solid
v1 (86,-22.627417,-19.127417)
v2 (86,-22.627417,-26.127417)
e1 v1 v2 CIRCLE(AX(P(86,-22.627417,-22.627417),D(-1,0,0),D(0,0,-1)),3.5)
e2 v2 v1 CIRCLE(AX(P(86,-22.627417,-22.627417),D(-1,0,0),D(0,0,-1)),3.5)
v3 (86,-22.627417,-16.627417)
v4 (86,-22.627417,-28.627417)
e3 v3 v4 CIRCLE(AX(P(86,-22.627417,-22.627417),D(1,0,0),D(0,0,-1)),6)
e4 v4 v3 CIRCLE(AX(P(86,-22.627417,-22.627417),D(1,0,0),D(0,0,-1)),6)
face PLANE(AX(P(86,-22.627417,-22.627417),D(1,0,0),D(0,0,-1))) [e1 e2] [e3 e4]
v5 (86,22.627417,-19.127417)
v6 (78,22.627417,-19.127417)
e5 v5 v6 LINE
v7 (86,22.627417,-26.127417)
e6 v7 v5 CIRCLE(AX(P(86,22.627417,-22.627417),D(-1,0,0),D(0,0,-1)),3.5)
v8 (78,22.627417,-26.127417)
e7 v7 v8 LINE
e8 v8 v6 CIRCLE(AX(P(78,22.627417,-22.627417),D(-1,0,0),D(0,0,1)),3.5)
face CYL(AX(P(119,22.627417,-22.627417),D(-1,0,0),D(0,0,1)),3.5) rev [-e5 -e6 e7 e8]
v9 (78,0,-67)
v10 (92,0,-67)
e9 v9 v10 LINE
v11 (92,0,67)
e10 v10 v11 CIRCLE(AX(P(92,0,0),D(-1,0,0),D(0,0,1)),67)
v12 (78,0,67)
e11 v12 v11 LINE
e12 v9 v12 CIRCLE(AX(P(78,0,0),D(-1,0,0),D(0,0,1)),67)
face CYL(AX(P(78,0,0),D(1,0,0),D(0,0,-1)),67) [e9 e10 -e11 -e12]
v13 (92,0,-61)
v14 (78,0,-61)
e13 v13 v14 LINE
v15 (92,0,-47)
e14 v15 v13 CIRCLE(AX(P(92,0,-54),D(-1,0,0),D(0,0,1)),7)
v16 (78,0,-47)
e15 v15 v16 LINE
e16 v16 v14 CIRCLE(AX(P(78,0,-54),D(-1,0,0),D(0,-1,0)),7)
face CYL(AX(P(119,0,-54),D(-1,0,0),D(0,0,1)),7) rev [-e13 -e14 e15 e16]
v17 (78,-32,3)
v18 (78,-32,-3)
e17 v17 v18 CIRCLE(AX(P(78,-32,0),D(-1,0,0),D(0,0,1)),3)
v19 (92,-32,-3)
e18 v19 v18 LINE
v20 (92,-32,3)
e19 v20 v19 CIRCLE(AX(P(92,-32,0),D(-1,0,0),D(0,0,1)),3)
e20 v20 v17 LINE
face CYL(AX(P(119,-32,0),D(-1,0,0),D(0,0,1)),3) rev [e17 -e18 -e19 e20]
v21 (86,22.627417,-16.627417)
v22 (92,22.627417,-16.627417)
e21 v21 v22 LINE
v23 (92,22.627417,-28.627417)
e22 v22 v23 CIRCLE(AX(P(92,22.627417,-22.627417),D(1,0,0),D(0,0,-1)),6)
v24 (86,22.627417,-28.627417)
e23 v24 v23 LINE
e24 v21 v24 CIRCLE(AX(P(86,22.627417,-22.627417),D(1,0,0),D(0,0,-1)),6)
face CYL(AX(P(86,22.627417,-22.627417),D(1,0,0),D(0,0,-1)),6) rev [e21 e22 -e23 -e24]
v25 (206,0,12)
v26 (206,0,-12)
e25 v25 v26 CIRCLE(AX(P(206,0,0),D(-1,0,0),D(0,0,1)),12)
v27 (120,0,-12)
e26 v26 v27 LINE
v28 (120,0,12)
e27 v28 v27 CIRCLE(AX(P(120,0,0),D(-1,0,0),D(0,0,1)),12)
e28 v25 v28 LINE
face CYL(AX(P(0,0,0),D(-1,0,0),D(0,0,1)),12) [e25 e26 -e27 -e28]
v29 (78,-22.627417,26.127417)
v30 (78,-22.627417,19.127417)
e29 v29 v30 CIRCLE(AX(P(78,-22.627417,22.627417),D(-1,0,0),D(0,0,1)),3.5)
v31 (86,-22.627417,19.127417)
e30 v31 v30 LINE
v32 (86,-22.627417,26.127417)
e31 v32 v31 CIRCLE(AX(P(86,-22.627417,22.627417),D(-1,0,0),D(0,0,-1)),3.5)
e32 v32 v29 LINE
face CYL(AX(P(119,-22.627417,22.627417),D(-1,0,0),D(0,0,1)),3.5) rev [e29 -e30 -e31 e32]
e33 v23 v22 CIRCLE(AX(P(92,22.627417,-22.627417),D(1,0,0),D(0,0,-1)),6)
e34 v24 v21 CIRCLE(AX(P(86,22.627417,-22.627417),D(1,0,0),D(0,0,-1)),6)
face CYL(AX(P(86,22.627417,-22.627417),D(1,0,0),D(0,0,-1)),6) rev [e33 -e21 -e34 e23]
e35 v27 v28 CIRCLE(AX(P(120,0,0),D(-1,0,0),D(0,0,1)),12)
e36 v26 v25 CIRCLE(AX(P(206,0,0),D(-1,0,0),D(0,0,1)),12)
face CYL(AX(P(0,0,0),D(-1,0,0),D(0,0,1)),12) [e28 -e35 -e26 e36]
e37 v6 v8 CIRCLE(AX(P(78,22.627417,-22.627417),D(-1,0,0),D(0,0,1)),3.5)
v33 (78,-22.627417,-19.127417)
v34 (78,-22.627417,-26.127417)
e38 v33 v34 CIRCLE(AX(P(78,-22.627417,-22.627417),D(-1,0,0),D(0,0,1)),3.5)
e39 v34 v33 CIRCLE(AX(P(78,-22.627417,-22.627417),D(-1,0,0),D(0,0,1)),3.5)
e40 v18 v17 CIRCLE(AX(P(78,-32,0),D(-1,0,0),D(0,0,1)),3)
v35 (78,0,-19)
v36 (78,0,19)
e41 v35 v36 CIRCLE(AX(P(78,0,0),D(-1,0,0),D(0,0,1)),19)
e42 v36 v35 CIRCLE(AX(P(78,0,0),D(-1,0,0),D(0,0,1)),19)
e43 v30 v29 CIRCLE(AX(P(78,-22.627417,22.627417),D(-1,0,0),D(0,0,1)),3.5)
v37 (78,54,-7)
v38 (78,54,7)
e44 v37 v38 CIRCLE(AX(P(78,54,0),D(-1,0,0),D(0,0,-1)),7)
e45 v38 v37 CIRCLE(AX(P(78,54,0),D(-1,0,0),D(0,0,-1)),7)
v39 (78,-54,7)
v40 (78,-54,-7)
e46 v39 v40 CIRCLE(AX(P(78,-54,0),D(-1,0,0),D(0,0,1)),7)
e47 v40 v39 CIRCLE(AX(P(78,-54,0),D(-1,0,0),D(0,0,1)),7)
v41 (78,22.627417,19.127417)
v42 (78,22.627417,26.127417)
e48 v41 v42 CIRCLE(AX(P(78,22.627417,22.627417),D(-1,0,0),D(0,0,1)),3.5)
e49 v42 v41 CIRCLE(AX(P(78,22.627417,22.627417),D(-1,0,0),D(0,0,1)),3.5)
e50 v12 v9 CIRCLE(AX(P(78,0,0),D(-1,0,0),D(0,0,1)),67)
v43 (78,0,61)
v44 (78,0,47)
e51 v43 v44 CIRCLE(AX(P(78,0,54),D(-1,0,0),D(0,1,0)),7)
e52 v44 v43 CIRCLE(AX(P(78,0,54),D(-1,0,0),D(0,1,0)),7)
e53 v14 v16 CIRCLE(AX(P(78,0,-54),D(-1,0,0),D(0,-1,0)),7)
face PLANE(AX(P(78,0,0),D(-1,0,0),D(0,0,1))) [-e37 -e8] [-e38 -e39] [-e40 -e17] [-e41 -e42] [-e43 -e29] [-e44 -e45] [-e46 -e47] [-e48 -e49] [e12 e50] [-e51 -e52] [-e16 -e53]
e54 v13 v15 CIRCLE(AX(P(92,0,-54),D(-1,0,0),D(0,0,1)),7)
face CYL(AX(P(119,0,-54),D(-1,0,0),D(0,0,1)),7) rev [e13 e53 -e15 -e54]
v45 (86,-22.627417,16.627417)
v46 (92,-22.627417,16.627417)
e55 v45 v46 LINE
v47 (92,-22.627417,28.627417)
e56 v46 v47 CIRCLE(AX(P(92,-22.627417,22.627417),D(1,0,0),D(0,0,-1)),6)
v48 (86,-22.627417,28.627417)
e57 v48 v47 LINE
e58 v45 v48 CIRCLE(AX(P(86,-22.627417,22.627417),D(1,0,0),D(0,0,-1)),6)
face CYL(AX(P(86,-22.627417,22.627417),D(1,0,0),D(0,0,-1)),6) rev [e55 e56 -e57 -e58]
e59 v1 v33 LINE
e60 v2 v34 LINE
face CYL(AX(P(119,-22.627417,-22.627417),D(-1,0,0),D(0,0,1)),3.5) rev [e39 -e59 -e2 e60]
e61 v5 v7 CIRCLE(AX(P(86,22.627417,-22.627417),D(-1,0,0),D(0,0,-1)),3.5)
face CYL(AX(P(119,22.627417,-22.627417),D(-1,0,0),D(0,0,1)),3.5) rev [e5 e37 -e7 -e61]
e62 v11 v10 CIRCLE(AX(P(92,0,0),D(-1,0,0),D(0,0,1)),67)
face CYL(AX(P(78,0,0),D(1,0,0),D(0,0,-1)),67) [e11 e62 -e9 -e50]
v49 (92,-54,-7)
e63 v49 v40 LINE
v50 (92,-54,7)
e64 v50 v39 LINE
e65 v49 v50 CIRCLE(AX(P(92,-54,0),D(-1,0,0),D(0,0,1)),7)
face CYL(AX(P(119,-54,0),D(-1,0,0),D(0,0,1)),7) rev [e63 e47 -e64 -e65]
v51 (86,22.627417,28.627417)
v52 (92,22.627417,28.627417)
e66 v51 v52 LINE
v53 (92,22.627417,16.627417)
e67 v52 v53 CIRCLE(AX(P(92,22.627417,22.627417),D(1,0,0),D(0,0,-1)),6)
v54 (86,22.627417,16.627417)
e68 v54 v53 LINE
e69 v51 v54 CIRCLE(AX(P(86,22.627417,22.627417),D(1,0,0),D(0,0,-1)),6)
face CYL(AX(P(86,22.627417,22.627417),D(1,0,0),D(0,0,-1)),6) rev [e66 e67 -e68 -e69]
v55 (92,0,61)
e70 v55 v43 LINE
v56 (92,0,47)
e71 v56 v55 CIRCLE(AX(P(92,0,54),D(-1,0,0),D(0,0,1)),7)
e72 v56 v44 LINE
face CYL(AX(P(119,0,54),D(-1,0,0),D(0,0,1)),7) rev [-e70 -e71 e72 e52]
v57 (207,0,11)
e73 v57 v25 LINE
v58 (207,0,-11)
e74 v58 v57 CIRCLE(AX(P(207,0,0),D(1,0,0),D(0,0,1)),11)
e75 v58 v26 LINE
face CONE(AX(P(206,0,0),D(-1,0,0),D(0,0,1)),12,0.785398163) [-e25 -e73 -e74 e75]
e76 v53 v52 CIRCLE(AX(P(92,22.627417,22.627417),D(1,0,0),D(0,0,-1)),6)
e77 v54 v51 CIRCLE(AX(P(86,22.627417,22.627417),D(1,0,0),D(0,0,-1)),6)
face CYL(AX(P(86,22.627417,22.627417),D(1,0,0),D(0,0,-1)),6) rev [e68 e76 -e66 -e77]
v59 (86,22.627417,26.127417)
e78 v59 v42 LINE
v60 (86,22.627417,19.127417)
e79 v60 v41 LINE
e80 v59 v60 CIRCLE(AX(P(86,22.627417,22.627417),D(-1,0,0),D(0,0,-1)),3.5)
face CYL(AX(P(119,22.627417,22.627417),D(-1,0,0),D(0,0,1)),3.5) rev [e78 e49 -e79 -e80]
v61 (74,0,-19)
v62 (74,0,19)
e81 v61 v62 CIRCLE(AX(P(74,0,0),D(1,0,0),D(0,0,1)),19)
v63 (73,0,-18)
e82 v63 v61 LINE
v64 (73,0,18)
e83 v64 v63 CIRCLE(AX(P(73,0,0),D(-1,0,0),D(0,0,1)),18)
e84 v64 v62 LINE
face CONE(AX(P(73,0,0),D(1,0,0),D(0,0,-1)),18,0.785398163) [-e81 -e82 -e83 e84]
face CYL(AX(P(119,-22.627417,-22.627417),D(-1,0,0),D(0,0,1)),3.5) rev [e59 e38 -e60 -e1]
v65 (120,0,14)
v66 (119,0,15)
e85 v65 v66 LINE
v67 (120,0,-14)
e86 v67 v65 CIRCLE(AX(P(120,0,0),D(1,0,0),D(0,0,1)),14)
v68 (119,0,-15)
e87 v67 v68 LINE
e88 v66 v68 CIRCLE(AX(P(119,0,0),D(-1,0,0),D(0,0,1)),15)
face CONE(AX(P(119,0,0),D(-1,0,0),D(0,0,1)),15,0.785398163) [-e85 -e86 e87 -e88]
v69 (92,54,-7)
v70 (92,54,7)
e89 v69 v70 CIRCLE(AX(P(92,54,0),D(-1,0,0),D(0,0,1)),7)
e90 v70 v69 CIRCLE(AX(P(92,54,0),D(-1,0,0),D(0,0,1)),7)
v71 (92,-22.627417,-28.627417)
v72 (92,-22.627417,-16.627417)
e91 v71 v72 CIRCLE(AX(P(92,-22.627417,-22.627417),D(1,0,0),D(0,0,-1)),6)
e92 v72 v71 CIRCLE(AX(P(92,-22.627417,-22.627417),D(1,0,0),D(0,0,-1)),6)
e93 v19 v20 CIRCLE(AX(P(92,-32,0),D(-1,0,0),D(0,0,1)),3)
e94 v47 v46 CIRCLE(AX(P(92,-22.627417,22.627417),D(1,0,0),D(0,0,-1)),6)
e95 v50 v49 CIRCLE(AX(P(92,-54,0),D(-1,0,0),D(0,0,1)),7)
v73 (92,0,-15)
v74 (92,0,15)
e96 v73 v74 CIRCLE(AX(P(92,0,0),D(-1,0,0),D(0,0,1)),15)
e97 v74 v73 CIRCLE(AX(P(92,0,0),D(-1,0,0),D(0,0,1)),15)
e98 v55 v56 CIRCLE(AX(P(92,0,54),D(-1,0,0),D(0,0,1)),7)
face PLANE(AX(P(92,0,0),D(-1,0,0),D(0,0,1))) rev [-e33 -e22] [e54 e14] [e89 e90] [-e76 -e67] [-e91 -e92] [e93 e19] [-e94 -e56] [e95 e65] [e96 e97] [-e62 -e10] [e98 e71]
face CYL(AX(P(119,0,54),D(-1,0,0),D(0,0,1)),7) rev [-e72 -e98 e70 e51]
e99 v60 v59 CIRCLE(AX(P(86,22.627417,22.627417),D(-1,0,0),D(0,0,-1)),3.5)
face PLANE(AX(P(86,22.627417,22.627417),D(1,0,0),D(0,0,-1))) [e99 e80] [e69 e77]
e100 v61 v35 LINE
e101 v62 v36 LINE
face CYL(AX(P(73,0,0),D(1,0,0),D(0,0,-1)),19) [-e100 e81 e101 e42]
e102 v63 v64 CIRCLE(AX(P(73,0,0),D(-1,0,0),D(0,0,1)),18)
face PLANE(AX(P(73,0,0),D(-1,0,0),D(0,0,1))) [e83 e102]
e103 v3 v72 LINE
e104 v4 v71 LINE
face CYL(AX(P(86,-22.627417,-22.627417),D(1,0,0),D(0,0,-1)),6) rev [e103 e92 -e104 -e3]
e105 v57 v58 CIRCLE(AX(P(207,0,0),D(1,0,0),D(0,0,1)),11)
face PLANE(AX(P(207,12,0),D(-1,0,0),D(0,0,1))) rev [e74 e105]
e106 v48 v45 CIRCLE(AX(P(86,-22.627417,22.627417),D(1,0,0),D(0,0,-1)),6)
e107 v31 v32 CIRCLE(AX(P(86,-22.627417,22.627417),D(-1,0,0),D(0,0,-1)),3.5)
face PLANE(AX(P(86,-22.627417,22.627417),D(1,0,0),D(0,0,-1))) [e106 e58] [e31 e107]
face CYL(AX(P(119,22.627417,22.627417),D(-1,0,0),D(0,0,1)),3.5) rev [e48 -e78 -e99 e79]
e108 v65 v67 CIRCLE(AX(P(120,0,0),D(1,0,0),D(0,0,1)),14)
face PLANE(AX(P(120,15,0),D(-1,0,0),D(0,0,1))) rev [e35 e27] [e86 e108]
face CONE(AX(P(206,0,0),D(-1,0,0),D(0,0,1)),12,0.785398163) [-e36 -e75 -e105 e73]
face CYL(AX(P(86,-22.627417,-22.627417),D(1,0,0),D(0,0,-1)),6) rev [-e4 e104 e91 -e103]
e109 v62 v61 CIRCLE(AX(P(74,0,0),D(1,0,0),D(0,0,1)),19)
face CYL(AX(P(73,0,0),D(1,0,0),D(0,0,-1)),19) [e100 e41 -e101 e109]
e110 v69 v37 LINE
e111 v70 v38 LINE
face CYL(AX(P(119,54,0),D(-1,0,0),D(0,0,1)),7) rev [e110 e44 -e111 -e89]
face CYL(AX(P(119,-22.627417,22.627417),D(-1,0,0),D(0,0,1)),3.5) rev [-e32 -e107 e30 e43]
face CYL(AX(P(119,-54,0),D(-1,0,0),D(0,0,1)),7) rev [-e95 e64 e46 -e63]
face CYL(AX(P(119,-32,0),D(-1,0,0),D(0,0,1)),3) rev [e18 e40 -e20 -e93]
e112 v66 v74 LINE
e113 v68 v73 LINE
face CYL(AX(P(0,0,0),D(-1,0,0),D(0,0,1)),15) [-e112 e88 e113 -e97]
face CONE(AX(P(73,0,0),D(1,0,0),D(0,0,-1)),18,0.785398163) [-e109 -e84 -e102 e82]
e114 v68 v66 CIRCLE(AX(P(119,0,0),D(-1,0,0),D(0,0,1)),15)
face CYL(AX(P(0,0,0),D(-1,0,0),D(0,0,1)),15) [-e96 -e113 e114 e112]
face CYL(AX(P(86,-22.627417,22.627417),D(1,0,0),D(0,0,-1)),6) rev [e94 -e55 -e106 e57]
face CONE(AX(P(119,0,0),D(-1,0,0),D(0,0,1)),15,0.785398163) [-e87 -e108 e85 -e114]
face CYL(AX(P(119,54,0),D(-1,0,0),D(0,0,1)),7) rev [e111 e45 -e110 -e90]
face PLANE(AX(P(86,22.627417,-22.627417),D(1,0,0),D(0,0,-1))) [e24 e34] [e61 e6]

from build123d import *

# Parameters (mm, degrees)
SKETCH2_R           = 3.5
CUT_EXTRUDE1_DEPTH  = 27
SKETCH3_R           = 5.5
CUT_EXTRUDE2_DEPTH  = 6
CIRPATTERN1_COUNT   = 4
CHAMFER1_SIZE       = 1
SKETCH4_R           = 52.910606105
CUT_EXTRUDE3_DEPTH  = 128
SKETCH5_R           = 67
BOSS_EXTRUDE1_DEPTH = 14
SKETCH6_R           = 19
BOSS_EXTRUDE2_DEPTH = 5
SKETCH7_R           = 3
SKETCH7_R_2         = 3.5
CUT_EXTRUDE4_DEPTH  = 41
SKETCH8_R           = 6
CUT_EXTRUDE5_DEPTH  = 6
CHAMFER2_SIZE       = 1
SKETCH9_R           = 7
CUT_EXTRUDE6_DEPTH  = 41
CIRPATTERN2_COUNT   = 4


with BuildPart() as part:
    # Sketch1 → Revolve1 (revolve)
    with BuildSketch(Plane.XY, mode=Mode.PRIVATE) as revolve1_sk:
        Polygon((0, 0), (0, 8), (75, 8), (75, 17.5), (82, 17.5), (82, 34), (92, 34), (92, 15), (120, 15), (120, 12), (207, 12), (207, 0), align=None)
    revolve(revolve1_sk.sketch.rotate(Axis((0, 0, 0), (1, 0, 0)), 90), axis=Axis((0, 0, 0), (1, 0, 0)))

    # Sketch2 → Cut-Extrude1 (cut)
    with BuildSketch(Plane(origin=(92, 0, 0), x_dir=(0, 0, -1), z_dir=(1, 0, 0))):
        with Locations((0, 24.5)):
            Circle(SKETCH2_R)
    cut_extrude1 = extrude(amount=-CUT_EXTRUDE1_DEPTH, mode=Mode.SUBTRACT)

    # Sketch3 → Cut-Extrude2 (cut)
    with BuildSketch(Plane.ZY.offset(-82)):
        with Locations((0, 24.5)):
            Circle(SKETCH3_R)
    cut_extrude2 = extrude(amount=-CUT_EXTRUDE2_DEPTH, mode=Mode.SUBTRACT)

    # CirPattern1: Cut-Extrude1, Cut-Extrude2 ×4 about axis
    cirpattern1_axis = Axis((0, 0, 0), (1, 0, 0))
    add([cut_extrude1.rotate(cirpattern1_axis, i * 360 / CIRPATTERN1_COUNT) for i in range(1, CIRPATTERN1_COUNT)], mode=Mode.SUBTRACT)
    add([cut_extrude2.rotate(cirpattern1_axis, i * 360 / CIRPATTERN1_COUNT) for i in range(1, CIRPATTERN1_COUNT)], mode=Mode.SUBTRACT)

    # Chamfer1
    chamfer1_edges = [part.edges().sort_by_distance(p)[0] for p in [
        (82, 0, -34),
        (75, 0, -17.5),
        (75, 0, -8),
        (0, 0, -8),
        (207, 0, -12),
        (120, 0, -15),
    ]]
    chamfer(chamfer1_edges, length=CHAMFER1_SIZE)

    # Sketch4 → Cut-Extrude3 (cut)
    with BuildSketch(Plane(origin=(92, 0, 0), x_dir=(0, 0, -1), z_dir=(1, 0, 0))):
        Circle(SKETCH4_R)
    extrude(amount=-CUT_EXTRUDE3_DEPTH, mode=Mode.SUBTRACT)

    # Sketch5 → Boss-Extrude1 (add)
    with BuildSketch(Plane.ZY.offset(-92)):
        Circle(SKETCH5_R)
    extrude(amount=BOSS_EXTRUDE1_DEPTH)

    # Sketch6 → Boss-Extrude2 (add)
    with BuildSketch(Plane.ZY.offset(-78)):
        Circle(SKETCH6_R)
    extrude(amount=BOSS_EXTRUDE2_DEPTH)

    # Sketch7 → Cut-Extrude4 (cut)
    with BuildSketch(Plane.ZY.offset(-78)):
        with Locations((0, -32)):
            Circle(SKETCH7_R)
        with Locations((22.627416998, 22.627416998)):
            Circle(SKETCH7_R_2)
        with Locations((22.627416998, -22.627416998)):
            Circle(SKETCH7_R_2)
        with Locations((-22.627416998, -22.627416998)):
            Circle(SKETCH7_R_2)
        with Locations((-22.627416998, 22.627416998)):
            Circle(SKETCH7_R_2)
    extrude(amount=-CUT_EXTRUDE4_DEPTH, mode=Mode.SUBTRACT)

    # Sketch8 → Cut-Extrude5 (cut)
    with BuildSketch(Plane(origin=(92, 0, 0), x_dir=(0, 0, -1), z_dir=(1, 0, 0))):
        with Locations((22.627416998, 22.627416998)):
            Circle(SKETCH8_R)
        with Locations((22.627416998, -22.627416998)):
            Circle(SKETCH8_R)
        with Locations((-22.627416998, -22.627416998)):
            Circle(SKETCH8_R)
        with Locations((-22.627416998, 22.627416998)):
            Circle(SKETCH8_R)
    extrude(amount=-CUT_EXTRUDE5_DEPTH, mode=Mode.SUBTRACT)

    # Chamfer2
    chamfer2_edges = [part.edges().sort_by_distance(p)[0] for p in [
        (73, 0, -19),
    ]]
    chamfer(chamfer2_edges, length=CHAMFER2_SIZE)

    # Sketch9 → Cut-Extrude6 (cut)
    with BuildSketch(Plane.ZY.offset(-78)):
        with Locations((0, -54)):
            Circle(SKETCH9_R)
    cut_extrude6 = extrude(amount=-CUT_EXTRUDE6_DEPTH, mode=Mode.SUBTRACT)

    # CirPattern2: Cut-Extrude6 ×4 about axis
    cirpattern2_axis = Axis((0, 0, 0), (1, 0, 0))
    for i in range(1, CIRPATTERN2_COUNT):
        add(cut_extrude6.rotate(cirpattern2_axis, i * 360 / CIRPATTERN2_COUNT), mode=Mode.SUBTRACT)


solid = part.part
